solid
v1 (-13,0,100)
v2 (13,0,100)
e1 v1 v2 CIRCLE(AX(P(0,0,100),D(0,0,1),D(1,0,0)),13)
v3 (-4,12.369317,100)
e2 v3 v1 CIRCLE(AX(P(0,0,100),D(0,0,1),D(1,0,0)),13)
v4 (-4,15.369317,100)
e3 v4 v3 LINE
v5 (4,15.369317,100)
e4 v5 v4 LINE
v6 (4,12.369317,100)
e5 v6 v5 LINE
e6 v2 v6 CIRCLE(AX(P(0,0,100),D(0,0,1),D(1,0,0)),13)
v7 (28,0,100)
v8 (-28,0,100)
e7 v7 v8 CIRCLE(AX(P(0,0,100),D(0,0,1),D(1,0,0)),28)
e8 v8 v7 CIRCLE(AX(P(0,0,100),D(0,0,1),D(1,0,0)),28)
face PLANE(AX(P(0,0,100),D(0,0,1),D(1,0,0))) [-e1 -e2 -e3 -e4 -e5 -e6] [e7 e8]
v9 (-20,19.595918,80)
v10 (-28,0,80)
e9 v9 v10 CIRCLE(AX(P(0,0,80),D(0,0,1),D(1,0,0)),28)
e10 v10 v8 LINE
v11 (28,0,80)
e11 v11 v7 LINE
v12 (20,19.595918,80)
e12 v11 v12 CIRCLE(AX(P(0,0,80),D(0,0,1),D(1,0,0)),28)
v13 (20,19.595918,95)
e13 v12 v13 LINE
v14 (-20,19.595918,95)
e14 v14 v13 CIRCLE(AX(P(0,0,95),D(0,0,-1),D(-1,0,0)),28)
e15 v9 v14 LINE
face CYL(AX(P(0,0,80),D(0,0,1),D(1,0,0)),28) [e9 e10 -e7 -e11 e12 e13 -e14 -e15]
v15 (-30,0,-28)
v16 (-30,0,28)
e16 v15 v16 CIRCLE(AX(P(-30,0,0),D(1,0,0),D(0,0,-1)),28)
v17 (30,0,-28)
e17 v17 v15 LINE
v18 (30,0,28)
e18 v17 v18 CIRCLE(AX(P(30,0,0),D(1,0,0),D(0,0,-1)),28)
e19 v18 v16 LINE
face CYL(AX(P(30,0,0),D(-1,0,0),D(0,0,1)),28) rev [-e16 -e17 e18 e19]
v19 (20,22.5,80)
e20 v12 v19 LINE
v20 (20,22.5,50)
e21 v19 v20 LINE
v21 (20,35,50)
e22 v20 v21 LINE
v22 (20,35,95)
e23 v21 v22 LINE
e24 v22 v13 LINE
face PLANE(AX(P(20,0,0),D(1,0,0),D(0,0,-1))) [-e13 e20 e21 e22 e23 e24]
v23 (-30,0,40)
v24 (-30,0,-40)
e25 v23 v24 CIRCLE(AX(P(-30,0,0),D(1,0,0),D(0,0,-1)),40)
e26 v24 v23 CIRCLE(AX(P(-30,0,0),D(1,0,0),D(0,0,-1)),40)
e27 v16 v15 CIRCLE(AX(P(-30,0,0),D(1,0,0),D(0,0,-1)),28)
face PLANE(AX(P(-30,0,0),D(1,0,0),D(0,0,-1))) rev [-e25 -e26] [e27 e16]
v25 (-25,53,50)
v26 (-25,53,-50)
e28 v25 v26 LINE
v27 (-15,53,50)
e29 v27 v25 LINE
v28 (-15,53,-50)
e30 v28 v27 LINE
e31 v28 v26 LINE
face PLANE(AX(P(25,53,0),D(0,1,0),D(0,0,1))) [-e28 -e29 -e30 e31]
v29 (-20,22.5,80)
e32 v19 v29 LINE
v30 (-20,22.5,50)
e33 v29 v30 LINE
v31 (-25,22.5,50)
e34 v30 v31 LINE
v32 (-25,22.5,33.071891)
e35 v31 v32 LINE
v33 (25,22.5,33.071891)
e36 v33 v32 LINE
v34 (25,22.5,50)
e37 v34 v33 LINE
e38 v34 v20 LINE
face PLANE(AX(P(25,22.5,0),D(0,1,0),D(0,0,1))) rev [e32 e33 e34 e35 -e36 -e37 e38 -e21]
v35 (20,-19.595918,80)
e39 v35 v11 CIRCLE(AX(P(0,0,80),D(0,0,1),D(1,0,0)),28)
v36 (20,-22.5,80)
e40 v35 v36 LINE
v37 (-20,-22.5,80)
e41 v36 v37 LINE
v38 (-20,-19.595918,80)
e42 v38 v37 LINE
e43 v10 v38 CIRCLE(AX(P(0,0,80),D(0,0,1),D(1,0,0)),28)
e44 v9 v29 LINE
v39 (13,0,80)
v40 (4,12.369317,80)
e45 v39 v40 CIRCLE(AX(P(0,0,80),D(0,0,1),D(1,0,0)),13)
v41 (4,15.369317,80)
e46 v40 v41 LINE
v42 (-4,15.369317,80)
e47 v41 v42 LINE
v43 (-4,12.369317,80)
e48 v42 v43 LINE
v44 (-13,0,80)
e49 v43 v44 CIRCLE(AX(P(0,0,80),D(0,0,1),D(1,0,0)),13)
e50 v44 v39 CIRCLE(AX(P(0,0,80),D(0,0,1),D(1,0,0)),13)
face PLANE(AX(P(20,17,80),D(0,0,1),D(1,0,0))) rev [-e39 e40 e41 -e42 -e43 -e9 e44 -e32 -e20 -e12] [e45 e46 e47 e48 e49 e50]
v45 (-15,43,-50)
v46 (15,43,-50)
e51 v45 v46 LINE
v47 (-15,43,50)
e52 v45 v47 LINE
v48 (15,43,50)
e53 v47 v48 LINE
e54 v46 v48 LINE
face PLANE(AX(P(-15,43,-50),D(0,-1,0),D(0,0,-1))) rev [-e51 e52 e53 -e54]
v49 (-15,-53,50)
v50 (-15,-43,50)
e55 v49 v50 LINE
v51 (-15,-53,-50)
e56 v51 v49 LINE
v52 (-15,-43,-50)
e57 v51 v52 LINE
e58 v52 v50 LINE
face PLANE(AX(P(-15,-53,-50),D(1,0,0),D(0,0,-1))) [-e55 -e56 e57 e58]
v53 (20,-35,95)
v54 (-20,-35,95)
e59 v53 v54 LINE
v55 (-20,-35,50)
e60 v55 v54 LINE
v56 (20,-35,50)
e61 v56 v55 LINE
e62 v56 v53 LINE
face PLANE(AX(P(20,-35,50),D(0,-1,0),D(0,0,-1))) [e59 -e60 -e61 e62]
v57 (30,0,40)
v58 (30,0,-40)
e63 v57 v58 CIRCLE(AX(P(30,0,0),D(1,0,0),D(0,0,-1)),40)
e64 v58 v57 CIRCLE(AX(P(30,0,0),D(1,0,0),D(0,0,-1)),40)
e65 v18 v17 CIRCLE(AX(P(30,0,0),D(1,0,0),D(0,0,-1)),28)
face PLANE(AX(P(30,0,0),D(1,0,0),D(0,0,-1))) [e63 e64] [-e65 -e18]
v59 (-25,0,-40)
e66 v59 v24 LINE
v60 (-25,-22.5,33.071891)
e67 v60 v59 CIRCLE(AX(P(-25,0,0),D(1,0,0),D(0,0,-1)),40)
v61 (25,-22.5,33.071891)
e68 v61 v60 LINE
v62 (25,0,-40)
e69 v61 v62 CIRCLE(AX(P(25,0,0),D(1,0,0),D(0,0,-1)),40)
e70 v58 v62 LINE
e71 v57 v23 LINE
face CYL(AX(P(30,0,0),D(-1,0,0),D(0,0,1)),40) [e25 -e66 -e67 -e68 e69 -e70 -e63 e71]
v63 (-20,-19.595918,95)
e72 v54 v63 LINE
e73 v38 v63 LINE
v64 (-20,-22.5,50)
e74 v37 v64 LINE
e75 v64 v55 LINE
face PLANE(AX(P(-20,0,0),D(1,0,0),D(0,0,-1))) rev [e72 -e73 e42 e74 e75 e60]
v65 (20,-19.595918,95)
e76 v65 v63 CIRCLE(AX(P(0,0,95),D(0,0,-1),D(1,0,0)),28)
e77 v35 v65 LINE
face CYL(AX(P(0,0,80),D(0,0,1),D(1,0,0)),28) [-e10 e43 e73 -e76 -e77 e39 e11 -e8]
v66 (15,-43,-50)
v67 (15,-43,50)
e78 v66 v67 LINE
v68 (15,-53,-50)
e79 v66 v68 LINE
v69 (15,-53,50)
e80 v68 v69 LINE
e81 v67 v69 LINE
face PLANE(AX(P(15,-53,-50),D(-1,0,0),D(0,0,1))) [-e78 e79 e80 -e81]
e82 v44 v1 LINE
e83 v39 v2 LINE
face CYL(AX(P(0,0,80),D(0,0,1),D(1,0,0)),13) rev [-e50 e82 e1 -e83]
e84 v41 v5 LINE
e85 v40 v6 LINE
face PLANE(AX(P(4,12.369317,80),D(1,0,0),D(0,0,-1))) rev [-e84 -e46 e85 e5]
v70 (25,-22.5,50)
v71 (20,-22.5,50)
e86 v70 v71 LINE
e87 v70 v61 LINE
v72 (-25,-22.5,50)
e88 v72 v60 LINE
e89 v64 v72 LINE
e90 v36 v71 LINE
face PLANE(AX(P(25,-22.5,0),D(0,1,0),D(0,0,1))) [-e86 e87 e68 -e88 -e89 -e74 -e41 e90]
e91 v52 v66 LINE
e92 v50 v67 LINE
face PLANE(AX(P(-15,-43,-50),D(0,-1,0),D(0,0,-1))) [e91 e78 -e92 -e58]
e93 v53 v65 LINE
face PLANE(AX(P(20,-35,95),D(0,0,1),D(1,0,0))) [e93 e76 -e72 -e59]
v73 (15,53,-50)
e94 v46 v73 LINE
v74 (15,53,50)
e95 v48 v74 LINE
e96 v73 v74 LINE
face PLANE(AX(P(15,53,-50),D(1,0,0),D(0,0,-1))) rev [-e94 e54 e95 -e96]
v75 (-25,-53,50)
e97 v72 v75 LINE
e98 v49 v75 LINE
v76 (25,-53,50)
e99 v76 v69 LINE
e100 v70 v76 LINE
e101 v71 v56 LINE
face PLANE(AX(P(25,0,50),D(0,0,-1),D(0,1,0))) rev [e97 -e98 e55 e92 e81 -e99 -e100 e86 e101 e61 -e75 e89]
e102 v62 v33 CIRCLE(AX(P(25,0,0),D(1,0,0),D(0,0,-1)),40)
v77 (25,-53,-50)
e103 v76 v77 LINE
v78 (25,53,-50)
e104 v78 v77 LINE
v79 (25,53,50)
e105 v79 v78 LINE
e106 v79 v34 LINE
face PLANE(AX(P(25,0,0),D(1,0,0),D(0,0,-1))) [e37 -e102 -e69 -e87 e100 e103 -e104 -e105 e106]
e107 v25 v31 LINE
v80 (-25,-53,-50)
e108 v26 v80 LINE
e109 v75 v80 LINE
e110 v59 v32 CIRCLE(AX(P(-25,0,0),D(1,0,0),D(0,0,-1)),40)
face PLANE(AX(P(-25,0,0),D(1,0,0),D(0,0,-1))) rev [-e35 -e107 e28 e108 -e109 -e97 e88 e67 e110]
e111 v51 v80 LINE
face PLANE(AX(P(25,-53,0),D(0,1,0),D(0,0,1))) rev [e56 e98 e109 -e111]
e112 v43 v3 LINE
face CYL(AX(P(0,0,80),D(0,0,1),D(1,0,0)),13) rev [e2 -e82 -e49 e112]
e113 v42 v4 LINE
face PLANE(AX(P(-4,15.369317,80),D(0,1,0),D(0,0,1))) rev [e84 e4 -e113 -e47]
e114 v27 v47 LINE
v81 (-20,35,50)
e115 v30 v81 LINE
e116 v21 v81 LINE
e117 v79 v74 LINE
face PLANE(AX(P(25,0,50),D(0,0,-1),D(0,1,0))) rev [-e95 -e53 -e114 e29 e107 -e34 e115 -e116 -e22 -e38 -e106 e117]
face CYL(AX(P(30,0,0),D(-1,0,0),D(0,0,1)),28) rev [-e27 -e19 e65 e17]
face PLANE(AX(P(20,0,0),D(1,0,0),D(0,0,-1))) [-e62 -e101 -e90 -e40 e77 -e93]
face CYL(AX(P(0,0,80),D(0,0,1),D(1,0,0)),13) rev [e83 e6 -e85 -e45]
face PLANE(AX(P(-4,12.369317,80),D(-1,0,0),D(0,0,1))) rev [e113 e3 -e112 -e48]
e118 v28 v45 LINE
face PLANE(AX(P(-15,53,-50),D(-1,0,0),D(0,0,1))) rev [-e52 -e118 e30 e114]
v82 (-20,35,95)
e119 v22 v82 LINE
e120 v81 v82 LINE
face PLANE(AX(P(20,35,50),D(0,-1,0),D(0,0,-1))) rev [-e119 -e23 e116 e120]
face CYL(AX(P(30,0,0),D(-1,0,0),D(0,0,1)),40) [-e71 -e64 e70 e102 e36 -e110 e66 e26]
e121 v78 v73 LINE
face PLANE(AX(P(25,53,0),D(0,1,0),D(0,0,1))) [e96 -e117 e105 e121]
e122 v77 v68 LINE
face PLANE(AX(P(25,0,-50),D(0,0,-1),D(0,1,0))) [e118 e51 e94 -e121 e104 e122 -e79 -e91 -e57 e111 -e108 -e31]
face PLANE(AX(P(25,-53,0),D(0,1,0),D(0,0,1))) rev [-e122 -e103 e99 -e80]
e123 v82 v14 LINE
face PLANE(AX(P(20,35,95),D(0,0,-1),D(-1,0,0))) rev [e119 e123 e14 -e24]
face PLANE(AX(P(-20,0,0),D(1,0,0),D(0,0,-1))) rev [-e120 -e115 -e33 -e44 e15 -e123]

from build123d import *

# Parameters (mm, degrees)
HOUSING_BODY_SKETCH_R   = 40
HOUSING_BODY_SKETCH_R_2 = 28
HOUSING_BODY_DEPTH      = 30
MOUNTING_FLANGE_DEPTH   = 25
KEYED_START             = 100
KEYED_HUB_SKETCH_R      = 28
KEYED_HUB_56_DEPTH      = 20
SIDE_RIB_DEPTH          = 20
SLOT_CUT_SKETCH_W       = 30
SLOT_CUT_SKETCH_H       = 10
SLOT_CUT_10X30_DEPTH    = 118.08543889


with BuildPart() as part:
    # Housing Body Sketch → Housing Body (new, symmetric)
    with BuildSketch(Plane(origin=(0, 0, 0), x_dir=(0, 0, -1), z_dir=(1, 0, 0))):
        Circle(HOUSING_BODY_SKETCH_R)
        Circle(HOUSING_BODY_SKETCH_R_2, mode=Mode.SUBTRACT)
    extrude(amount=HOUSING_BODY_DEPTH, both=True)

    # Mounting Flange Sketch → Mounting Flange (add, symmetric)
    with BuildSketch(Plane(origin=(0, 0, 0), x_dir=(0, 0, -1), z_dir=(1, 0, 0))):
        with BuildLine():
            Line((-33.071891388, -22.5), (-50, -22.5))
            Line((-50, -22.5), (-50, -53))
            Line((-50, -53), (50, -53))
            Line((50, -53), (50, 53))
            Line((50, 53), (-50, 53))
            Line((-50, 53), (-50, 22.5))
            Line((-50, 22.5), (-33.071891388, 22.5))
            ThreePointArc((-33.071891388, 22.5), (11.771243445, 38.228756555), (40, 0))
            ThreePointArc((40, 0), (11.771243445, -38.228756555), (-33.071891388, -22.5))
        make_face()
    extrude(amount=MOUNTING_FLANGE_DEPTH, both=True)



with BuildPart() as body_2:
    # Keyed Hub Sketch → Keyed Hub Ø56 (new body)
    with BuildSketch(Plane.XY.offset(KEYED_START)):
        Circle(KEYED_HUB_SKETCH_R)
        with BuildLine():
            Line((-4, 12.369316877), (-4, 15.369316877))
            Line((-4, 15.369316877), (4, 15.369316877))
            Line((4, 15.369316877), (4, 12.369316877))
            ThreePointArc((4, 12.369316877), (0, -13), (-4, 12.369316877))
        make_face(mode=Mode.SUBTRACT)
    extrude(amount=-KEYED_HUB_56_DEPTH)


with BuildPart() as part_1:
    add(part.part)

    add(body_2.part)  # Side Rib merges body 2
    # Side Rib Sketch → Side Rib (add, symmetric)
    with BuildSketch(Plane(origin=(0, 0, 0), x_dir=(0, 0, -1), z_dir=(1, 0, 0))):
        Polygon((-50, 35), (-95, 35), (-95, 17), (-80, 17), (-80, 22.5), (-50, 22.5), align=None)
    side_rib = extrude(amount=SIDE_RIB_DEPTH, both=True)

    # Side Rib Mirror: Side Rib across plane
    add(side_rib.mirror(Plane.ZX))

    # Slot Cut Sketch → Slot Cut 10x30 (cut, through all)
    with BuildSketch(Plane.XY.offset(50)):
        with Locations((0, 48)):
            Rectangle(SLOT_CUT_SKETCH_W, SLOT_CUT_SKETCH_H)
    slot_cut_10x30 = extrude(amount=-SLOT_CUT_10X30_DEPTH, mode=Mode.SUBTRACT)

    # Slot Cut Mirror: Slot Cut 10x30 across plane
    add(slot_cut_10x30.mirror(Plane.ZX), mode=Mode.SUBTRACT)


solid = part_1.part
